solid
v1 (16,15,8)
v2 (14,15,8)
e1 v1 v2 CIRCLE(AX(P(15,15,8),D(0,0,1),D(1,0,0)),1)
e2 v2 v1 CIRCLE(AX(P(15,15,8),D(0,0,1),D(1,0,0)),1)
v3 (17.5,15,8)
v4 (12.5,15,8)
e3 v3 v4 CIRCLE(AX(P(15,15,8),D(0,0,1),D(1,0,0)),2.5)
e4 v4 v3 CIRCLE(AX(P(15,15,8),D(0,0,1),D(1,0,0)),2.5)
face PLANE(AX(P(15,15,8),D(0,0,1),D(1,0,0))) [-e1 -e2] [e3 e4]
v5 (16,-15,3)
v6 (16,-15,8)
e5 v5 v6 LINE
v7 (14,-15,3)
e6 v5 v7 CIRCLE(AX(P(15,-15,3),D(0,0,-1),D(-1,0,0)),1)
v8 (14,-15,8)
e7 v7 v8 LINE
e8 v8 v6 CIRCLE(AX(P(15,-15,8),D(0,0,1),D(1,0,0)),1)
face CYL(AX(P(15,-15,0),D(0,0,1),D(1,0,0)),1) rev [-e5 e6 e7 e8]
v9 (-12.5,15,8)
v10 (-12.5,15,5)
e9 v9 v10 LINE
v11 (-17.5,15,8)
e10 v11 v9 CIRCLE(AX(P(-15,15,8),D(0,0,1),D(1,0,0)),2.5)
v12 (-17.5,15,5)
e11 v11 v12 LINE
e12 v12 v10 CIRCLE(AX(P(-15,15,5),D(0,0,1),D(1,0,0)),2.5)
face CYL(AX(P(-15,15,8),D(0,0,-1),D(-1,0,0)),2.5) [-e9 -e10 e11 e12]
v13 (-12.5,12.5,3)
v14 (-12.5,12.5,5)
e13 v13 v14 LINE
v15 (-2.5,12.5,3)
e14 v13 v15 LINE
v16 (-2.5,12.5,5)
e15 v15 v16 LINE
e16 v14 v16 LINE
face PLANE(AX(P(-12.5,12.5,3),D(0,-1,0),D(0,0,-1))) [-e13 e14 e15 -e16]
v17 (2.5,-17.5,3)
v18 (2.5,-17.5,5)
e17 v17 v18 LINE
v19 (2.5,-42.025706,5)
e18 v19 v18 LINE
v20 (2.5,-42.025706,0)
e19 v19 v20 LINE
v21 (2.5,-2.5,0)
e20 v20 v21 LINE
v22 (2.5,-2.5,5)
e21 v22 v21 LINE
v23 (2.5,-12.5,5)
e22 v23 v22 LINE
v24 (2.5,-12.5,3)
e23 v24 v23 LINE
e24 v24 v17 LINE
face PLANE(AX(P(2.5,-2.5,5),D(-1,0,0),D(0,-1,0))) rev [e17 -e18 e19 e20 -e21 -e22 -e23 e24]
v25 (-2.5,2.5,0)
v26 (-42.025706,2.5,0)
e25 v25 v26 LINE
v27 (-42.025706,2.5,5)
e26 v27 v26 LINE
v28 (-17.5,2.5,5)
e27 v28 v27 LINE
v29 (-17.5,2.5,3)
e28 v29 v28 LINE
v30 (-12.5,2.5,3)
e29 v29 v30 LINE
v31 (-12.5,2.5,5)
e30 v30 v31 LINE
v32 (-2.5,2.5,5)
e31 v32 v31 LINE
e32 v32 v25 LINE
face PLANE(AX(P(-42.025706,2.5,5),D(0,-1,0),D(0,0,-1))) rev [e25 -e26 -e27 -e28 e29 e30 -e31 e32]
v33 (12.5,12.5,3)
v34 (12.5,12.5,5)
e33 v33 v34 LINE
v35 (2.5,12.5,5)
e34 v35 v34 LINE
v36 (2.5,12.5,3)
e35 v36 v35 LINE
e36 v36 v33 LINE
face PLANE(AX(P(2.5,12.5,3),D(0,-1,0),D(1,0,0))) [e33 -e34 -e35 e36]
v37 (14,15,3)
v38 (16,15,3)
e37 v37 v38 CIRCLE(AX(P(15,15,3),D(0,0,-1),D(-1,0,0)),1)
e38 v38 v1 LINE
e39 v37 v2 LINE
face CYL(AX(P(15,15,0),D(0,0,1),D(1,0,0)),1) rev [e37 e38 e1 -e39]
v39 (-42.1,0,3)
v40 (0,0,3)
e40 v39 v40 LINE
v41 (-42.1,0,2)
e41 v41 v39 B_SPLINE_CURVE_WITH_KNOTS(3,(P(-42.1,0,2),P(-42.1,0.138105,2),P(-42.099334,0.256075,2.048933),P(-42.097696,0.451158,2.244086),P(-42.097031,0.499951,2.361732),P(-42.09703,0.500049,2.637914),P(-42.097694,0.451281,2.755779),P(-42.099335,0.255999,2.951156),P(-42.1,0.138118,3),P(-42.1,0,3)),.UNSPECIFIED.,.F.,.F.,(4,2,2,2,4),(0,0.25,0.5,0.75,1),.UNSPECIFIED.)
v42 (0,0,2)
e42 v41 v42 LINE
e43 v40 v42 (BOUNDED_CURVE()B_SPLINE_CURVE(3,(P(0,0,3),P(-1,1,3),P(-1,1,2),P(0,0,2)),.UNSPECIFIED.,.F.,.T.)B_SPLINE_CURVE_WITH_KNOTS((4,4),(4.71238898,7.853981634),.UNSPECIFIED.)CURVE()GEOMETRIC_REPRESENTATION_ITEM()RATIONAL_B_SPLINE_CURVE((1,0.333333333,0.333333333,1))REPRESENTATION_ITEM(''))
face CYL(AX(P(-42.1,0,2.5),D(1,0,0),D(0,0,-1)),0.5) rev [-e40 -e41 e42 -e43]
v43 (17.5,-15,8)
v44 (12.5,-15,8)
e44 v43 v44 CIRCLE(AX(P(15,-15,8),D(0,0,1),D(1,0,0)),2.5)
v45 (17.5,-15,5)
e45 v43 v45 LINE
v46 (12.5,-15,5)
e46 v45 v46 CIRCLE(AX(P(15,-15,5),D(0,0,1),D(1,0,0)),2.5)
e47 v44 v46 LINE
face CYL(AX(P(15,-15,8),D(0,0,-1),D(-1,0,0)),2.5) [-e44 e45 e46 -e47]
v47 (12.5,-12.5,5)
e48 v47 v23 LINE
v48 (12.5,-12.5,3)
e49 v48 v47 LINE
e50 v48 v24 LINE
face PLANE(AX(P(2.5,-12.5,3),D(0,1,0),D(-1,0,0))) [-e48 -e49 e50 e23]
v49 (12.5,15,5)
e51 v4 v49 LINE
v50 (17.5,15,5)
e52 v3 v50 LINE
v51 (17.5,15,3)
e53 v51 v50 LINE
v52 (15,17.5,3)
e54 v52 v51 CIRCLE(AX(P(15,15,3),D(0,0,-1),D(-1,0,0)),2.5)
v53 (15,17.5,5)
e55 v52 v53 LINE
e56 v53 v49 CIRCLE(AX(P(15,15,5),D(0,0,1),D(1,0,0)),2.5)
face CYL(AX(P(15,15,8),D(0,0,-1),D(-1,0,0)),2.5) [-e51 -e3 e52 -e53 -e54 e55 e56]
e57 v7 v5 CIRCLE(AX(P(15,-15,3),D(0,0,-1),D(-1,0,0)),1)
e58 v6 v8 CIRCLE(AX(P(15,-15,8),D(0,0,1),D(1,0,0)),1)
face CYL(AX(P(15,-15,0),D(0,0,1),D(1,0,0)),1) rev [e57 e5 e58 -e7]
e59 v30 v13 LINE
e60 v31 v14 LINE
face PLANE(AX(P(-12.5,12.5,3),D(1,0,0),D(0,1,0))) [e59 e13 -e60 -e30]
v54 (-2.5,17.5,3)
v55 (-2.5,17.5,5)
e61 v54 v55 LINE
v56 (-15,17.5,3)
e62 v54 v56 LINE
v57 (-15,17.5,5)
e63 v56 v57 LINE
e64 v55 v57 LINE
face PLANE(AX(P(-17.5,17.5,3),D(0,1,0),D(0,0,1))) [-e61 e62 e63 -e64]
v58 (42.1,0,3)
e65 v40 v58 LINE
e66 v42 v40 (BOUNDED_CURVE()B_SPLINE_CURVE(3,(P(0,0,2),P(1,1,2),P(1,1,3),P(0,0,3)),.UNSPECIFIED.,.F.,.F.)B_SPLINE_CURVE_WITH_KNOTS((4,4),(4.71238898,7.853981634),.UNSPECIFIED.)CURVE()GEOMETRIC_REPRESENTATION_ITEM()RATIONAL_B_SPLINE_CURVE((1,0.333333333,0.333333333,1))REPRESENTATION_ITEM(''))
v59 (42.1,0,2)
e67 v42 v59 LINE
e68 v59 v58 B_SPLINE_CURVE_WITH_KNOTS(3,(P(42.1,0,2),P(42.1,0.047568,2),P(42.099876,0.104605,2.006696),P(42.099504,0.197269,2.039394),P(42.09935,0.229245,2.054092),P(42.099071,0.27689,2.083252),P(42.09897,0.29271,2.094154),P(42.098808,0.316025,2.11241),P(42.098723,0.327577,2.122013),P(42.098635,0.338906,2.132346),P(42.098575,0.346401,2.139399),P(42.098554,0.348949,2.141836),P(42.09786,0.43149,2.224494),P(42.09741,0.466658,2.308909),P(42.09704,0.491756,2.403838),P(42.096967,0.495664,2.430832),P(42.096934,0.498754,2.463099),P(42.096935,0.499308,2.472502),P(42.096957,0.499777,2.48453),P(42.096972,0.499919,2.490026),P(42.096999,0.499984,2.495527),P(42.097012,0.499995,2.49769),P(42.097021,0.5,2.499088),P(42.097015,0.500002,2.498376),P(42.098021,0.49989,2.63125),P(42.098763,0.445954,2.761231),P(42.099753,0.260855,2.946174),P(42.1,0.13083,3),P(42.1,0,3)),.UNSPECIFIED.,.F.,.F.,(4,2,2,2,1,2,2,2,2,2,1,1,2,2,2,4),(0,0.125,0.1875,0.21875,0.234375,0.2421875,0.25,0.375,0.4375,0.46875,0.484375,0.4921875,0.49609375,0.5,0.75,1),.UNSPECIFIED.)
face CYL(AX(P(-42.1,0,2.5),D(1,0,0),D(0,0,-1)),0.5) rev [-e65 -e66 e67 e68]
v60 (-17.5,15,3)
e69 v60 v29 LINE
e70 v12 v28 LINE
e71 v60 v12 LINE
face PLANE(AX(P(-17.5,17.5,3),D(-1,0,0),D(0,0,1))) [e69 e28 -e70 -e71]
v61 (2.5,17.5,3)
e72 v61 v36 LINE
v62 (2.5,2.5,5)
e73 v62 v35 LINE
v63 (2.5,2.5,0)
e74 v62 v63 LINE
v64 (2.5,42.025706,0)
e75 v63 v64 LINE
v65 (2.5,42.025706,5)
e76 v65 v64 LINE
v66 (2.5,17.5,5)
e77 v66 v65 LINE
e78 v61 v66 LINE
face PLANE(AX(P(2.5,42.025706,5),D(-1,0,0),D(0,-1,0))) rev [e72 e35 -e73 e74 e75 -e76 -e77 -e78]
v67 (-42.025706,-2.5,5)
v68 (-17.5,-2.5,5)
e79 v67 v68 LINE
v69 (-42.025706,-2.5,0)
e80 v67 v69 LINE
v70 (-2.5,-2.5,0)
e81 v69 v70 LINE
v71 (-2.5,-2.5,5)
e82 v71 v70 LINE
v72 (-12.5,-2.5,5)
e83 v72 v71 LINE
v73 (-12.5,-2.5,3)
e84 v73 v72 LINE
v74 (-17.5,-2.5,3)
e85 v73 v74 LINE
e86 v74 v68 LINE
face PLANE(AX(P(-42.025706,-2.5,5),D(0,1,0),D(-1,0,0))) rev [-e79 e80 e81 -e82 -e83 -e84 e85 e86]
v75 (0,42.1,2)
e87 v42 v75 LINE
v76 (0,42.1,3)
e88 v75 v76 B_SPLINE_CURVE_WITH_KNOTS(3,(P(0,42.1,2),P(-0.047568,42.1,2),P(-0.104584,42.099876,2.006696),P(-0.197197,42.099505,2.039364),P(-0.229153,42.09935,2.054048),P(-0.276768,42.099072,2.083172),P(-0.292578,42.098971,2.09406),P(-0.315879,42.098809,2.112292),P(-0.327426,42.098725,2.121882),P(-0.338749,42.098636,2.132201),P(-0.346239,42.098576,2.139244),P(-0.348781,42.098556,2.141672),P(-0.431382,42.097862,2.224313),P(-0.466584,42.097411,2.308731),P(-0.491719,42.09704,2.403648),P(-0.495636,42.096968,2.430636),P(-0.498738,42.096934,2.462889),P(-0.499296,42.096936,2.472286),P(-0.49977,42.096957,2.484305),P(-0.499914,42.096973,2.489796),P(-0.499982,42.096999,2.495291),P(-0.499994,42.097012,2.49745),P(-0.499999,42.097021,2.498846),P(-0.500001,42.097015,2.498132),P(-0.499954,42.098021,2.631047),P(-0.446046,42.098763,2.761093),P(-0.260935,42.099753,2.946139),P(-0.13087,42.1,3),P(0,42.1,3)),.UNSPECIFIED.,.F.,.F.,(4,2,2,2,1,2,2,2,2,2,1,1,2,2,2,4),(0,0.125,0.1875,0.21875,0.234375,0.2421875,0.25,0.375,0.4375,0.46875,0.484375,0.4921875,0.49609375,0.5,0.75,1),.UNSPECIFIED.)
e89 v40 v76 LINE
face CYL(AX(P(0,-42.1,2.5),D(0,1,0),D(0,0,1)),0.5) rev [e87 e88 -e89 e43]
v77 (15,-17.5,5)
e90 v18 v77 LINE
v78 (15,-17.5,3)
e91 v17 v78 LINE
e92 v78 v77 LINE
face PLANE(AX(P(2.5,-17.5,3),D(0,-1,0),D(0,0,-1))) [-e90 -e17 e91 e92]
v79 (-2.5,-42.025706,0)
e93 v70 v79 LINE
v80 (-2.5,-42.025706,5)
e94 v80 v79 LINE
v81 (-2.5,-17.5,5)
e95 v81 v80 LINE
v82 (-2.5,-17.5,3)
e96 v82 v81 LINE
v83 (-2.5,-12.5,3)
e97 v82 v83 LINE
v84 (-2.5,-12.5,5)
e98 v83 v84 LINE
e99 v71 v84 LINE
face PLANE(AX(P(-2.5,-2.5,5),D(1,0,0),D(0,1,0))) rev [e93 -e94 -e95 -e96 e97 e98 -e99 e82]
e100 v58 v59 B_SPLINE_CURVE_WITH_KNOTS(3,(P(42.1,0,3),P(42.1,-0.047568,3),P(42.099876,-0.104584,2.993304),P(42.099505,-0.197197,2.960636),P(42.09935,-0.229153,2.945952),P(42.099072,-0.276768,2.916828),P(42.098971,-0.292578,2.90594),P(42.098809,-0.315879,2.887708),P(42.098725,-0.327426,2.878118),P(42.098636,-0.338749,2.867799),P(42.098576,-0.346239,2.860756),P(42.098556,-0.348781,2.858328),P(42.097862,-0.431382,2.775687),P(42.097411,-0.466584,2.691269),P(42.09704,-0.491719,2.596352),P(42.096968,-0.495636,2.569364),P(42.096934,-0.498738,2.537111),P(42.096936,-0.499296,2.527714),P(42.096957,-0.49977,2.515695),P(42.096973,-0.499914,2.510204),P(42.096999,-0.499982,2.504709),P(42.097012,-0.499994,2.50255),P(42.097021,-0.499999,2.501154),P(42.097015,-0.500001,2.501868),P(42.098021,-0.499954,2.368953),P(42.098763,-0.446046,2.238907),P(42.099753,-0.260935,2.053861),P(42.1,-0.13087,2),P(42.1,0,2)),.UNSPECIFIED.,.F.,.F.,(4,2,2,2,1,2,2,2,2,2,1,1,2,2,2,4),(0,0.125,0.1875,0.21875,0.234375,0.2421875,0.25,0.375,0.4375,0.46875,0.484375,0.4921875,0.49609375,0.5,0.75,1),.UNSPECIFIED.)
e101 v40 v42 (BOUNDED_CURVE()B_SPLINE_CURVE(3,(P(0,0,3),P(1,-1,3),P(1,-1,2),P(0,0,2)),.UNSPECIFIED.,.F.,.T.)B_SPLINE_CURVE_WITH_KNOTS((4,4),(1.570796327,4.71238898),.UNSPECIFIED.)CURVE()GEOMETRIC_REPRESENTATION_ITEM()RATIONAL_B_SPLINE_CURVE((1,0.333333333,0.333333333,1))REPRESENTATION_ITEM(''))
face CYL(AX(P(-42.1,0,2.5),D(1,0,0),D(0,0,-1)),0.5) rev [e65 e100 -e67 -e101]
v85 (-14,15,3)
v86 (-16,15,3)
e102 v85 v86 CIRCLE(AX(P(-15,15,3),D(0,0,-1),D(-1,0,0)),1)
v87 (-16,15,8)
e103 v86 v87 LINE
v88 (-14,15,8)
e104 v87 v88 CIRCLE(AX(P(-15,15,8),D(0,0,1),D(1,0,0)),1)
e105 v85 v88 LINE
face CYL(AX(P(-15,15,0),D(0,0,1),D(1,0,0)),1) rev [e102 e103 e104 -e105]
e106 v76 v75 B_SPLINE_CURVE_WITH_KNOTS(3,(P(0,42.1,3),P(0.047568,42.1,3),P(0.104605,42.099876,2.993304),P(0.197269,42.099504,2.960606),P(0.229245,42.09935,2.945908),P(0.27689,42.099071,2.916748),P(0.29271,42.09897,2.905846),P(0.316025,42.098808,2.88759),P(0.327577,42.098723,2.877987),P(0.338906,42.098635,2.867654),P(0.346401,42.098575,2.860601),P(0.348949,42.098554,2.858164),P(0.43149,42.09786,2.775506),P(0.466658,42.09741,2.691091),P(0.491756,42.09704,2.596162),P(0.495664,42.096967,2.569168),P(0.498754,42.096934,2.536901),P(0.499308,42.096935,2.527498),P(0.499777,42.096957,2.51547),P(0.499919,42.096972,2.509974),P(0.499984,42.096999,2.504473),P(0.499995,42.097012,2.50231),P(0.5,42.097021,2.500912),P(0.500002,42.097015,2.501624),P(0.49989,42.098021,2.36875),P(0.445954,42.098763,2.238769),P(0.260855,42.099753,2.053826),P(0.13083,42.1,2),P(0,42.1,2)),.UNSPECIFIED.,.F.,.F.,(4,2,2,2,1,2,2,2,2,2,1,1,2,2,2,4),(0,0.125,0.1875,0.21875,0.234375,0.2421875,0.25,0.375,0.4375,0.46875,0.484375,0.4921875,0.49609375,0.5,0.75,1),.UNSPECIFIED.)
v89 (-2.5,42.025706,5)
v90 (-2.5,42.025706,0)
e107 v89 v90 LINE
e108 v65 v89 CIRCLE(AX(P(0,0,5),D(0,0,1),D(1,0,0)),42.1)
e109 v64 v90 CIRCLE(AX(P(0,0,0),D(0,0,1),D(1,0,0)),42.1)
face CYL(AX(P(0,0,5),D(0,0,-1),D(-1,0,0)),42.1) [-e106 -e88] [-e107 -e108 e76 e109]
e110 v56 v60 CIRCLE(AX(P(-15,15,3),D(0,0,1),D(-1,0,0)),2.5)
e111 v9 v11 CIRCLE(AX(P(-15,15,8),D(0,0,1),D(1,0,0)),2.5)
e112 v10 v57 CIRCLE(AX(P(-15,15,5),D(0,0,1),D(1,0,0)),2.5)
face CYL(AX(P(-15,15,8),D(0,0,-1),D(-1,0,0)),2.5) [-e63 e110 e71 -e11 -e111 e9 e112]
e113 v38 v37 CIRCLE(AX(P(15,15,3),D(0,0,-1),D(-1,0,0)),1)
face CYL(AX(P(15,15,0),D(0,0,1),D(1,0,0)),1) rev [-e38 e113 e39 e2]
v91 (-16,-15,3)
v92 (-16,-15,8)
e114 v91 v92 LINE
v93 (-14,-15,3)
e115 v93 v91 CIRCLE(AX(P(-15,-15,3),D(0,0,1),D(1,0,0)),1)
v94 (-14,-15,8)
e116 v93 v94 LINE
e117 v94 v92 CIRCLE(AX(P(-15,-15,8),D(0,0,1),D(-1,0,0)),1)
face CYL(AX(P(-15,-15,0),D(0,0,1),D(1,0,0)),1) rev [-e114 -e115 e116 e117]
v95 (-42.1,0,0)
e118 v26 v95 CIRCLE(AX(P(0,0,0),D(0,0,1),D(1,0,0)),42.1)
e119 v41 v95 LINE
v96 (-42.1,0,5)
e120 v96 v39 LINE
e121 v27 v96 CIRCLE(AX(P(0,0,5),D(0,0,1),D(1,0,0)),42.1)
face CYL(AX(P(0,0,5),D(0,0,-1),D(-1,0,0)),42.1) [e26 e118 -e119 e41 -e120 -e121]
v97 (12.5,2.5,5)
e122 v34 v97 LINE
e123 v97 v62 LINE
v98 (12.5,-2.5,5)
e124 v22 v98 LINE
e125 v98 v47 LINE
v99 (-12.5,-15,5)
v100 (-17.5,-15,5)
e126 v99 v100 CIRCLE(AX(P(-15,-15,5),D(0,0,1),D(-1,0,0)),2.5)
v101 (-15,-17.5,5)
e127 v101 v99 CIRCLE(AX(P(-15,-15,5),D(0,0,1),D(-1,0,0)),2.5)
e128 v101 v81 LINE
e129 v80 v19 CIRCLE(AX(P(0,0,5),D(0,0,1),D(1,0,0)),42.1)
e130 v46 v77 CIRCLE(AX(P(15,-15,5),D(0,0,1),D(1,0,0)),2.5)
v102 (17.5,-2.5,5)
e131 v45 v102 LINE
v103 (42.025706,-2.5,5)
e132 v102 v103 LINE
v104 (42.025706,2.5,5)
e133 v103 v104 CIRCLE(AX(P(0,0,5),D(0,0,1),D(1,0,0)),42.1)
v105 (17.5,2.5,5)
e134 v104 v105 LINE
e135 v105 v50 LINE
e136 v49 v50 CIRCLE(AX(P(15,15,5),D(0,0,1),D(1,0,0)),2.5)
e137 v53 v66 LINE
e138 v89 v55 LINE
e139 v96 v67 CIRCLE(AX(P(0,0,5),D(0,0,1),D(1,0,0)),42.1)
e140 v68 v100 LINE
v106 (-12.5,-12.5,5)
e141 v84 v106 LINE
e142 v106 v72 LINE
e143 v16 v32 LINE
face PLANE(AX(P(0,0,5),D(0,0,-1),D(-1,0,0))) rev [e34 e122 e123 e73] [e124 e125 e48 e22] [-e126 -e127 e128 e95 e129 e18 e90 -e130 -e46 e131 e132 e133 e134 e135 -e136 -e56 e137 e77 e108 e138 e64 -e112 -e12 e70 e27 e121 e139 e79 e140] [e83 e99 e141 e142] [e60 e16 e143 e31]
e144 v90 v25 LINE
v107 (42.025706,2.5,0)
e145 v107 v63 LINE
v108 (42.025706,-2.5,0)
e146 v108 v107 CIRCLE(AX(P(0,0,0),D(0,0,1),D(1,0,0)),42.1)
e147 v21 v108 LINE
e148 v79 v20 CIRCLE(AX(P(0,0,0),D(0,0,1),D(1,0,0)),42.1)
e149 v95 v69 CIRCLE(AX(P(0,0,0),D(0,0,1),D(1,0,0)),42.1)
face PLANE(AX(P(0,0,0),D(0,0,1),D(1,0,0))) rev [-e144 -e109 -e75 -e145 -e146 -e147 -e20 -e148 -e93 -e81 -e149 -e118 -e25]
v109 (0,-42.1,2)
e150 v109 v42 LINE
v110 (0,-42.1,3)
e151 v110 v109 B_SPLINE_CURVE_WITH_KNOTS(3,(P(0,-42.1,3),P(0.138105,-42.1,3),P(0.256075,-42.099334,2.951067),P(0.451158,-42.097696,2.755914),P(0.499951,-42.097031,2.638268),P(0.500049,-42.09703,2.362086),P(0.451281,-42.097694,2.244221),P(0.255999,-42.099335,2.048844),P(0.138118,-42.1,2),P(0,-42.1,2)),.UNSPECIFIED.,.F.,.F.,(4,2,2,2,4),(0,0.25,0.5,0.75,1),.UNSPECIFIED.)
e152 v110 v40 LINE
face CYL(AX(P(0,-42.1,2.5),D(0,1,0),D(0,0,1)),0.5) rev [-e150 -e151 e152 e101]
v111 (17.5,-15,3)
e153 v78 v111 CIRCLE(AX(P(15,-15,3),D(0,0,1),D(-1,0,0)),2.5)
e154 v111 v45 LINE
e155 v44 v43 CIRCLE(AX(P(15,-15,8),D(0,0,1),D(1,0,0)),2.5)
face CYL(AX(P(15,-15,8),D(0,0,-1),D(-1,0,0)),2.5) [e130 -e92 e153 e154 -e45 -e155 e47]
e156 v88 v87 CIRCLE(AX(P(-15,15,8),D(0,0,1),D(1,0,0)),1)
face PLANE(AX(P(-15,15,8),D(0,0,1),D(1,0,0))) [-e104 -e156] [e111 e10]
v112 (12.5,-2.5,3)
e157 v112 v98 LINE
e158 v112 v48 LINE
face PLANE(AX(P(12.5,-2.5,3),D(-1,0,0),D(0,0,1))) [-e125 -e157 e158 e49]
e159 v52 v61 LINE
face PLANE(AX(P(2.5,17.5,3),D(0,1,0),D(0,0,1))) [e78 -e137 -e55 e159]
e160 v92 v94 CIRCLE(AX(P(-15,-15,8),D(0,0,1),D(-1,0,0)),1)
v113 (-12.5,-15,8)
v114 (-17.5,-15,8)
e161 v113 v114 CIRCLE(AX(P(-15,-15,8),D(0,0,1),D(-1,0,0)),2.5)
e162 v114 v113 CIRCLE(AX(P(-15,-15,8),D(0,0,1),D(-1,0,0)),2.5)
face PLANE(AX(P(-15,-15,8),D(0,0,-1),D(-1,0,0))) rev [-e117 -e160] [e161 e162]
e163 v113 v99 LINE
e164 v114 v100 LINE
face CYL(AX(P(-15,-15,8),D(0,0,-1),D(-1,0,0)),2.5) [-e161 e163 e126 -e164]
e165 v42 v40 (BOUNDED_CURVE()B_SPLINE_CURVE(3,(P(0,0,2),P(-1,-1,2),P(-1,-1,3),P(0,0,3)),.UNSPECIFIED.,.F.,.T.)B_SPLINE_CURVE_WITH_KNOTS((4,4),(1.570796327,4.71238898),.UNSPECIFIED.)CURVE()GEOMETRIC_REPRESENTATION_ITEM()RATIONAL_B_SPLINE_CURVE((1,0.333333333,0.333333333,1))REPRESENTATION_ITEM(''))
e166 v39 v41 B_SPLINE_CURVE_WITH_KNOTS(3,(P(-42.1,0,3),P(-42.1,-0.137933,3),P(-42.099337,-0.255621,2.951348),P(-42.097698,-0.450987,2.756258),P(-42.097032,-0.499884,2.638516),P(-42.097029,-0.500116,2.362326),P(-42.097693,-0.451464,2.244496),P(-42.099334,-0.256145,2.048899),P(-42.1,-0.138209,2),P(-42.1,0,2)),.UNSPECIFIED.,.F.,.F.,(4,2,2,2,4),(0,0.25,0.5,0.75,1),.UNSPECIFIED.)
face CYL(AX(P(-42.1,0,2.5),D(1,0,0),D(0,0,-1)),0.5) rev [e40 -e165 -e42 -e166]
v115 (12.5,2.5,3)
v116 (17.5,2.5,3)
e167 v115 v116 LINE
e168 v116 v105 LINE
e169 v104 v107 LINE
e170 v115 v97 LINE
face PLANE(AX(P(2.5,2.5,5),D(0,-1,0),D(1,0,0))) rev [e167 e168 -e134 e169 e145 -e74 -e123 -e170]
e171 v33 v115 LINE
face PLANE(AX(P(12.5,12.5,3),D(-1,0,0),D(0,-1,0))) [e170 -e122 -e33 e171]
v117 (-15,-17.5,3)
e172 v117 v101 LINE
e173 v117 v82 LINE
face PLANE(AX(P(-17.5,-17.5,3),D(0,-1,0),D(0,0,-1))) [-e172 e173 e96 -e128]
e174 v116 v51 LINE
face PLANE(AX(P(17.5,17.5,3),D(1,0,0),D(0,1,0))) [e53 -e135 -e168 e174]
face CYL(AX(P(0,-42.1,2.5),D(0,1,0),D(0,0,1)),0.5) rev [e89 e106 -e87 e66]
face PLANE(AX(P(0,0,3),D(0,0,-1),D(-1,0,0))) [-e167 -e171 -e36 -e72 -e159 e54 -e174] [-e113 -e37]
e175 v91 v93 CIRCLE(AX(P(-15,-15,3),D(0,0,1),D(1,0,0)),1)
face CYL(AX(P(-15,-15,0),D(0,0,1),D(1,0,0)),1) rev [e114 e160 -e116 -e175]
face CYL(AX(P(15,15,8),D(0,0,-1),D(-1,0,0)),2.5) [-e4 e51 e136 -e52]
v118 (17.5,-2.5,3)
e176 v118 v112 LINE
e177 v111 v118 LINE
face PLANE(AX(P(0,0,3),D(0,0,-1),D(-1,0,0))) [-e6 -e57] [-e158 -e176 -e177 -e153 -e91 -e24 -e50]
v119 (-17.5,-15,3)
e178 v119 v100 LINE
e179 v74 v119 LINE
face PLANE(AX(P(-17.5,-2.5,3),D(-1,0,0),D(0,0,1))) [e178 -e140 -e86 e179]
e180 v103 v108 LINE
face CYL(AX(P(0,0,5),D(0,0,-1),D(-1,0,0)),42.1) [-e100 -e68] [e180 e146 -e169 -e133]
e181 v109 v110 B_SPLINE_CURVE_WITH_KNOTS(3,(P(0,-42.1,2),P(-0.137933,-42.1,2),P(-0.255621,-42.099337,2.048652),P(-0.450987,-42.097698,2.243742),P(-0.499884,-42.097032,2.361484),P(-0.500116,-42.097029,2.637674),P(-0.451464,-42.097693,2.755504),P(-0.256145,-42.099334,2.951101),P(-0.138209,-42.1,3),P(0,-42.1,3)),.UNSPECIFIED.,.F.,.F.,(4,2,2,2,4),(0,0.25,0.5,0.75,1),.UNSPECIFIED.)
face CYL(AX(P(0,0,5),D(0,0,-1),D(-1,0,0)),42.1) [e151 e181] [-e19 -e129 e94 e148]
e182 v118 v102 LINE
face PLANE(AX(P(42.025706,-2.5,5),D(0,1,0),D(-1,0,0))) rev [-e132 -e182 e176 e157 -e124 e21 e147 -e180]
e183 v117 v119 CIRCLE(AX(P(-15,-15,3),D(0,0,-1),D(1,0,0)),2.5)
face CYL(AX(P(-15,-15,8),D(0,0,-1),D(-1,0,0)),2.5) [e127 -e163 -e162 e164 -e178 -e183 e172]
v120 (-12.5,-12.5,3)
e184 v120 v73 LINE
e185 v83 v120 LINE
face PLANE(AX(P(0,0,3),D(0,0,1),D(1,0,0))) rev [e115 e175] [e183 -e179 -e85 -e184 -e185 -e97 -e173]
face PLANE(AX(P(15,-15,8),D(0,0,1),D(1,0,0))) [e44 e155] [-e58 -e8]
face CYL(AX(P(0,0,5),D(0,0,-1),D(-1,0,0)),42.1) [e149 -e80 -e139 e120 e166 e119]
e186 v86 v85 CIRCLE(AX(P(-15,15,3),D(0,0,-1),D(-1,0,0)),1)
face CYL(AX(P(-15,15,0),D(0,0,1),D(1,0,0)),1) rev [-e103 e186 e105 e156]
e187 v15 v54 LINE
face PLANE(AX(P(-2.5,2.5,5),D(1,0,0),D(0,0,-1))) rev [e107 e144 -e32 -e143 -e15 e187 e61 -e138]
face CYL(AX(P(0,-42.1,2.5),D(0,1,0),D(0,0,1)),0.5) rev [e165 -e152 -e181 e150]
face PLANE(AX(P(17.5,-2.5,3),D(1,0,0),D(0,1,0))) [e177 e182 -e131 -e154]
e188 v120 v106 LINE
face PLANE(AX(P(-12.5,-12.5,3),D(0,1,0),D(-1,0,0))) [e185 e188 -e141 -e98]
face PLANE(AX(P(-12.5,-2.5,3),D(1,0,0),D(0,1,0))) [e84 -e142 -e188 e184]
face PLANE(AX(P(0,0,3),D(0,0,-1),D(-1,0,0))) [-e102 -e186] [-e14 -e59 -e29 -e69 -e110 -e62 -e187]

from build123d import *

# Parameters (mm, degrees)
BOSS_EXTRUDE1_DEPTH     = 5
BOSS_EXTRUDE2_DEPTH     = 2
BOSS_EXTRUDE2_2_DEPTH   = 2
BOSS_EXTRUDE2_3_DEPTH   = 2
BOSS_EXTRUDE2_4_DEPTH   = 2
SKETCH3_R               = 1
CUT_EXTRUDE1_DEPTH      = 60.747970677
SKETCH5_R               = 2.5
SKETCH5_R_2             = 1
BOSS_EXTRUDE3_DEPTH     = 3
CUT_EXTRUDE2_DEPTH      = 60.747970677
SKETCH12_R              = 2.5
BOSS_EXTRUDE4_DEPTH     = 3
SKETCH13_R              = 1
CUT_EXTRUDE3_DEPTH      = 61.073455036
CUT_EXTRUDE4_DEPTH      = 60.747970677
CUT_EXTRUDE5_DEPTH      = 61.073455036
CUT_EXTRUDE5_DEPTH_BACK = 61.073455036
SKETCH17_R              = 0.5
CUT_EXTRUDE6_DEPTH      = 61.073455106
CUT_EXTRUDE6_DEPTH_BACK = 61.073455106
SKETCH18_R              = 0.5


with BuildPart() as part:
    # Sketch1 → Boss-Extrude1 (new body)
    with BuildSketch(Plane.XY):
        with BuildLine():
            Line((-42.025706419, 2.5), (-2.5, 2.5))
            Line((-2.5, 2.5), (-2.5, 42.025706419))
            ThreePointArc((-2.5, 42.025706419), (0, 42.1), (2.5, 42.025706419))
            Line((2.5, 42.025706419), (2.5, 2.5))
            Line((2.5, 2.5), (42.025706419, 2.5))
            ThreePointArc((42.025706419, 2.5), (42.1, 0), (42.025706419, -2.5))
            Line((42.025706419, -2.5), (2.5, -2.5))
            Line((2.5, -2.5), (2.5, -42.025706419))
            ThreePointArc((2.5, -42.025706419), (0, -42.1), (-2.5, -42.025706419))
            Line((-2.5, -42.025706419), (-2.5, -2.5))
            Line((-2.5, -2.5), (-42.025706419, -2.5))
            ThreePointArc((-42.025706419, -2.5), (-42.1, 0), (-42.025706419, 2.5))
        make_face()
    extrude(amount=BOSS_EXTRUDE1_DEPTH)



with BuildPart() as body_2:
    # Sketch2 → Boss-Extrude2 (new body)
    with BuildSketch(Plane.XY.offset(5)):
        Polygon((2.5, 12.5), (12.5, 12.5), (12.5, 2.5), (17.5, 2.5), (17.5, 17.5), (2.5, 17.5), align=None)
    extrude(amount=-BOSS_EXTRUDE2_DEPTH)

    # Sketch3 → Cut-Extrude1 (cut, through all)
    with BuildSketch(Plane.XY.offset(5)):
        with Locations((15, 15)):
            Circle(SKETCH3_R)
    extrude(amount=-CUT_EXTRUDE1_DEPTH, mode=Mode.SUBTRACT)


with BuildPart() as body_3:
    # Sketch2 → Boss-Extrude2 2 (new body)
    with BuildSketch(Plane.XY.offset(5)):
        Polygon((-12.5, 12.5), (-2.5, 12.5), (-2.5, 17.5), (-17.5, 17.5), (-17.5, 2.5), (-12.5, 2.5), align=None)
    extrude(amount=-BOSS_EXTRUDE2_2_DEPTH)



with BuildPart() as body_4:
    # Sketch2 → Boss-Extrude2 3 (new body)
    with BuildSketch(Plane.XY.offset(5)):
        Polygon((-12.5, -12.5), (-2.5, -12.5), (-2.5, -17.5), (-17.5, -17.5), (-17.5, -2.5), (-12.5, -2.5), align=None)
    extrude(amount=-BOSS_EXTRUDE2_3_DEPTH)


with BuildPart() as body_5:
    # Sketch2 → Boss-Extrude2 4 (new body)
    with BuildSketch(Plane.XY.offset(5)):
        Polygon((12.5, -2.5), (12.5, -12.5), (2.5, -12.5), (2.5, -17.5), (17.5, -17.5), (17.5, -2.5), align=None)
    extrude(amount=-BOSS_EXTRUDE2_4_DEPTH)


with BuildPart() as part_1:
    add(part.part)

    add(body_2.part)  # Boss-Extrude3 merges body 2
    # Sketch5 → Boss-Extrude3 (add)
    with BuildSketch(Plane.XY.offset(5)):
        with Locations((15, 15)):
            Circle(SKETCH5_R)
        with Locations((15, 15)):
            Circle(SKETCH5_R_2, mode=Mode.SUBTRACT)
    extrude(amount=BOSS_EXTRUDE3_DEPTH)

    # Sketch6 → Cut-Extrude2 (cut, through all)
    with BuildSketch(Plane.XY.offset(5)):
        with BuildLine():
            ThreePointArc((17.5, 15), (16.767766953, 16.767766953), (15, 17.5))
            Line((15, 17.5), (17.5, 17.5))
            Line((17.5, 17.5), (17.5, 15))
        make_face()
    extrude(amount=-CUT_EXTRUDE2_DEPTH, mode=Mode.SUBTRACT)


with BuildPart() as body_3_1:
    add(body_3.part)

    add(part_1.part)  # Boss-Extrude4 merges part

    add(body_5.part)  # Boss-Extrude4 merges body 5

    add(body_4.part)  # Boss-Extrude4 merges body 4
    # Sketch12 → Boss-Extrude4 (add)
    with BuildSketch(Plane.XY.offset(5)):
        with Locations((15, -15)):
            Circle(SKETCH12_R)
        with Locations(Location((-15, -15, 0), (0, 0, 180))):
            Circle(SKETCH12_R)
        with Locations(Location((-15, 15, 0), (0, 0, 180))):
            Circle(SKETCH12_R)
    extrude(amount=BOSS_EXTRUDE4_DEPTH)

    # Sketch13 → Cut-Extrude3 (cut, through all)
    with BuildSketch(Plane.XY.offset(8)):
        with Locations((15, -15)):
            Circle(SKETCH13_R)
        with Locations((-15, -15)):
            Circle(SKETCH13_R)
        with Locations((-15, 15)):
            Circle(SKETCH13_R)
    extrude(amount=-CUT_EXTRUDE3_DEPTH, mode=Mode.SUBTRACT)

    # Sketch14 → Cut-Extrude4 (cut, through all)
    with BuildSketch(Plane.XY.offset(5)):
        with BuildLine():
            Line((-15, 17.5), (-17.5, 17.5))
            Line((-17.5, 17.5), (-17.5, 15))
            ThreePointArc((-17.5, 15), (-16.767766953, 16.767766953), (-15, 17.5))
        make_face()
        with BuildLine():
            Line((-17.5, -15), (-17.5, -17.5))
            Line((-17.5, -17.5), (-15, -17.5))
            ThreePointArc((-15, -17.5), (-16.767766953, -16.767766953), (-17.5, -15))
        make_face()
        with BuildLine():
            Line((15, -17.5), (17.5, -17.5))
            Line((17.5, -17.5), (17.5, -15))
            ThreePointArc((17.5, -15), (16.767766953, -16.767766953), (15, -17.5))
        make_face()
    extrude(amount=-CUT_EXTRUDE4_DEPTH, mode=Mode.SUBTRACT)

    # Sketch17 → Cut-Extrude5 (cut, two sides: drawn at the far end of the back side and taken through both)
    with BuildSketch(Plane(origin=(0, 0, 0), x_dir=(1, 0, 0), z_dir=(0, 1, 0)).offset(-CUT_EXTRUDE5_DEPTH_BACK)):
        with Locations(Location((0, -2.5, 0), (0, 0, 270))):
            Circle(SKETCH17_R)
    extrude(amount=CUT_EXTRUDE5_DEPTH + CUT_EXTRUDE5_DEPTH_BACK, mode=Mode.SUBTRACT)

    # Sketch18 → Cut-Extrude6 (cut, two sides: drawn at the far end of the back side and taken through both)
    with BuildSketch(Plane(origin=(0, 0, 0), x_dir=(0, 0, -1), z_dir=(1, 0, 0)).offset(-CUT_EXTRUDE6_DEPTH_BACK)):
        with Locations((-2.5, 0)):
            Circle(SKETCH18_R)
    extrude(amount=CUT_EXTRUDE6_DEPTH + CUT_EXTRUDE6_DEPTH_BACK, mode=Mode.SUBTRACT)


solid = body_3_1.part
